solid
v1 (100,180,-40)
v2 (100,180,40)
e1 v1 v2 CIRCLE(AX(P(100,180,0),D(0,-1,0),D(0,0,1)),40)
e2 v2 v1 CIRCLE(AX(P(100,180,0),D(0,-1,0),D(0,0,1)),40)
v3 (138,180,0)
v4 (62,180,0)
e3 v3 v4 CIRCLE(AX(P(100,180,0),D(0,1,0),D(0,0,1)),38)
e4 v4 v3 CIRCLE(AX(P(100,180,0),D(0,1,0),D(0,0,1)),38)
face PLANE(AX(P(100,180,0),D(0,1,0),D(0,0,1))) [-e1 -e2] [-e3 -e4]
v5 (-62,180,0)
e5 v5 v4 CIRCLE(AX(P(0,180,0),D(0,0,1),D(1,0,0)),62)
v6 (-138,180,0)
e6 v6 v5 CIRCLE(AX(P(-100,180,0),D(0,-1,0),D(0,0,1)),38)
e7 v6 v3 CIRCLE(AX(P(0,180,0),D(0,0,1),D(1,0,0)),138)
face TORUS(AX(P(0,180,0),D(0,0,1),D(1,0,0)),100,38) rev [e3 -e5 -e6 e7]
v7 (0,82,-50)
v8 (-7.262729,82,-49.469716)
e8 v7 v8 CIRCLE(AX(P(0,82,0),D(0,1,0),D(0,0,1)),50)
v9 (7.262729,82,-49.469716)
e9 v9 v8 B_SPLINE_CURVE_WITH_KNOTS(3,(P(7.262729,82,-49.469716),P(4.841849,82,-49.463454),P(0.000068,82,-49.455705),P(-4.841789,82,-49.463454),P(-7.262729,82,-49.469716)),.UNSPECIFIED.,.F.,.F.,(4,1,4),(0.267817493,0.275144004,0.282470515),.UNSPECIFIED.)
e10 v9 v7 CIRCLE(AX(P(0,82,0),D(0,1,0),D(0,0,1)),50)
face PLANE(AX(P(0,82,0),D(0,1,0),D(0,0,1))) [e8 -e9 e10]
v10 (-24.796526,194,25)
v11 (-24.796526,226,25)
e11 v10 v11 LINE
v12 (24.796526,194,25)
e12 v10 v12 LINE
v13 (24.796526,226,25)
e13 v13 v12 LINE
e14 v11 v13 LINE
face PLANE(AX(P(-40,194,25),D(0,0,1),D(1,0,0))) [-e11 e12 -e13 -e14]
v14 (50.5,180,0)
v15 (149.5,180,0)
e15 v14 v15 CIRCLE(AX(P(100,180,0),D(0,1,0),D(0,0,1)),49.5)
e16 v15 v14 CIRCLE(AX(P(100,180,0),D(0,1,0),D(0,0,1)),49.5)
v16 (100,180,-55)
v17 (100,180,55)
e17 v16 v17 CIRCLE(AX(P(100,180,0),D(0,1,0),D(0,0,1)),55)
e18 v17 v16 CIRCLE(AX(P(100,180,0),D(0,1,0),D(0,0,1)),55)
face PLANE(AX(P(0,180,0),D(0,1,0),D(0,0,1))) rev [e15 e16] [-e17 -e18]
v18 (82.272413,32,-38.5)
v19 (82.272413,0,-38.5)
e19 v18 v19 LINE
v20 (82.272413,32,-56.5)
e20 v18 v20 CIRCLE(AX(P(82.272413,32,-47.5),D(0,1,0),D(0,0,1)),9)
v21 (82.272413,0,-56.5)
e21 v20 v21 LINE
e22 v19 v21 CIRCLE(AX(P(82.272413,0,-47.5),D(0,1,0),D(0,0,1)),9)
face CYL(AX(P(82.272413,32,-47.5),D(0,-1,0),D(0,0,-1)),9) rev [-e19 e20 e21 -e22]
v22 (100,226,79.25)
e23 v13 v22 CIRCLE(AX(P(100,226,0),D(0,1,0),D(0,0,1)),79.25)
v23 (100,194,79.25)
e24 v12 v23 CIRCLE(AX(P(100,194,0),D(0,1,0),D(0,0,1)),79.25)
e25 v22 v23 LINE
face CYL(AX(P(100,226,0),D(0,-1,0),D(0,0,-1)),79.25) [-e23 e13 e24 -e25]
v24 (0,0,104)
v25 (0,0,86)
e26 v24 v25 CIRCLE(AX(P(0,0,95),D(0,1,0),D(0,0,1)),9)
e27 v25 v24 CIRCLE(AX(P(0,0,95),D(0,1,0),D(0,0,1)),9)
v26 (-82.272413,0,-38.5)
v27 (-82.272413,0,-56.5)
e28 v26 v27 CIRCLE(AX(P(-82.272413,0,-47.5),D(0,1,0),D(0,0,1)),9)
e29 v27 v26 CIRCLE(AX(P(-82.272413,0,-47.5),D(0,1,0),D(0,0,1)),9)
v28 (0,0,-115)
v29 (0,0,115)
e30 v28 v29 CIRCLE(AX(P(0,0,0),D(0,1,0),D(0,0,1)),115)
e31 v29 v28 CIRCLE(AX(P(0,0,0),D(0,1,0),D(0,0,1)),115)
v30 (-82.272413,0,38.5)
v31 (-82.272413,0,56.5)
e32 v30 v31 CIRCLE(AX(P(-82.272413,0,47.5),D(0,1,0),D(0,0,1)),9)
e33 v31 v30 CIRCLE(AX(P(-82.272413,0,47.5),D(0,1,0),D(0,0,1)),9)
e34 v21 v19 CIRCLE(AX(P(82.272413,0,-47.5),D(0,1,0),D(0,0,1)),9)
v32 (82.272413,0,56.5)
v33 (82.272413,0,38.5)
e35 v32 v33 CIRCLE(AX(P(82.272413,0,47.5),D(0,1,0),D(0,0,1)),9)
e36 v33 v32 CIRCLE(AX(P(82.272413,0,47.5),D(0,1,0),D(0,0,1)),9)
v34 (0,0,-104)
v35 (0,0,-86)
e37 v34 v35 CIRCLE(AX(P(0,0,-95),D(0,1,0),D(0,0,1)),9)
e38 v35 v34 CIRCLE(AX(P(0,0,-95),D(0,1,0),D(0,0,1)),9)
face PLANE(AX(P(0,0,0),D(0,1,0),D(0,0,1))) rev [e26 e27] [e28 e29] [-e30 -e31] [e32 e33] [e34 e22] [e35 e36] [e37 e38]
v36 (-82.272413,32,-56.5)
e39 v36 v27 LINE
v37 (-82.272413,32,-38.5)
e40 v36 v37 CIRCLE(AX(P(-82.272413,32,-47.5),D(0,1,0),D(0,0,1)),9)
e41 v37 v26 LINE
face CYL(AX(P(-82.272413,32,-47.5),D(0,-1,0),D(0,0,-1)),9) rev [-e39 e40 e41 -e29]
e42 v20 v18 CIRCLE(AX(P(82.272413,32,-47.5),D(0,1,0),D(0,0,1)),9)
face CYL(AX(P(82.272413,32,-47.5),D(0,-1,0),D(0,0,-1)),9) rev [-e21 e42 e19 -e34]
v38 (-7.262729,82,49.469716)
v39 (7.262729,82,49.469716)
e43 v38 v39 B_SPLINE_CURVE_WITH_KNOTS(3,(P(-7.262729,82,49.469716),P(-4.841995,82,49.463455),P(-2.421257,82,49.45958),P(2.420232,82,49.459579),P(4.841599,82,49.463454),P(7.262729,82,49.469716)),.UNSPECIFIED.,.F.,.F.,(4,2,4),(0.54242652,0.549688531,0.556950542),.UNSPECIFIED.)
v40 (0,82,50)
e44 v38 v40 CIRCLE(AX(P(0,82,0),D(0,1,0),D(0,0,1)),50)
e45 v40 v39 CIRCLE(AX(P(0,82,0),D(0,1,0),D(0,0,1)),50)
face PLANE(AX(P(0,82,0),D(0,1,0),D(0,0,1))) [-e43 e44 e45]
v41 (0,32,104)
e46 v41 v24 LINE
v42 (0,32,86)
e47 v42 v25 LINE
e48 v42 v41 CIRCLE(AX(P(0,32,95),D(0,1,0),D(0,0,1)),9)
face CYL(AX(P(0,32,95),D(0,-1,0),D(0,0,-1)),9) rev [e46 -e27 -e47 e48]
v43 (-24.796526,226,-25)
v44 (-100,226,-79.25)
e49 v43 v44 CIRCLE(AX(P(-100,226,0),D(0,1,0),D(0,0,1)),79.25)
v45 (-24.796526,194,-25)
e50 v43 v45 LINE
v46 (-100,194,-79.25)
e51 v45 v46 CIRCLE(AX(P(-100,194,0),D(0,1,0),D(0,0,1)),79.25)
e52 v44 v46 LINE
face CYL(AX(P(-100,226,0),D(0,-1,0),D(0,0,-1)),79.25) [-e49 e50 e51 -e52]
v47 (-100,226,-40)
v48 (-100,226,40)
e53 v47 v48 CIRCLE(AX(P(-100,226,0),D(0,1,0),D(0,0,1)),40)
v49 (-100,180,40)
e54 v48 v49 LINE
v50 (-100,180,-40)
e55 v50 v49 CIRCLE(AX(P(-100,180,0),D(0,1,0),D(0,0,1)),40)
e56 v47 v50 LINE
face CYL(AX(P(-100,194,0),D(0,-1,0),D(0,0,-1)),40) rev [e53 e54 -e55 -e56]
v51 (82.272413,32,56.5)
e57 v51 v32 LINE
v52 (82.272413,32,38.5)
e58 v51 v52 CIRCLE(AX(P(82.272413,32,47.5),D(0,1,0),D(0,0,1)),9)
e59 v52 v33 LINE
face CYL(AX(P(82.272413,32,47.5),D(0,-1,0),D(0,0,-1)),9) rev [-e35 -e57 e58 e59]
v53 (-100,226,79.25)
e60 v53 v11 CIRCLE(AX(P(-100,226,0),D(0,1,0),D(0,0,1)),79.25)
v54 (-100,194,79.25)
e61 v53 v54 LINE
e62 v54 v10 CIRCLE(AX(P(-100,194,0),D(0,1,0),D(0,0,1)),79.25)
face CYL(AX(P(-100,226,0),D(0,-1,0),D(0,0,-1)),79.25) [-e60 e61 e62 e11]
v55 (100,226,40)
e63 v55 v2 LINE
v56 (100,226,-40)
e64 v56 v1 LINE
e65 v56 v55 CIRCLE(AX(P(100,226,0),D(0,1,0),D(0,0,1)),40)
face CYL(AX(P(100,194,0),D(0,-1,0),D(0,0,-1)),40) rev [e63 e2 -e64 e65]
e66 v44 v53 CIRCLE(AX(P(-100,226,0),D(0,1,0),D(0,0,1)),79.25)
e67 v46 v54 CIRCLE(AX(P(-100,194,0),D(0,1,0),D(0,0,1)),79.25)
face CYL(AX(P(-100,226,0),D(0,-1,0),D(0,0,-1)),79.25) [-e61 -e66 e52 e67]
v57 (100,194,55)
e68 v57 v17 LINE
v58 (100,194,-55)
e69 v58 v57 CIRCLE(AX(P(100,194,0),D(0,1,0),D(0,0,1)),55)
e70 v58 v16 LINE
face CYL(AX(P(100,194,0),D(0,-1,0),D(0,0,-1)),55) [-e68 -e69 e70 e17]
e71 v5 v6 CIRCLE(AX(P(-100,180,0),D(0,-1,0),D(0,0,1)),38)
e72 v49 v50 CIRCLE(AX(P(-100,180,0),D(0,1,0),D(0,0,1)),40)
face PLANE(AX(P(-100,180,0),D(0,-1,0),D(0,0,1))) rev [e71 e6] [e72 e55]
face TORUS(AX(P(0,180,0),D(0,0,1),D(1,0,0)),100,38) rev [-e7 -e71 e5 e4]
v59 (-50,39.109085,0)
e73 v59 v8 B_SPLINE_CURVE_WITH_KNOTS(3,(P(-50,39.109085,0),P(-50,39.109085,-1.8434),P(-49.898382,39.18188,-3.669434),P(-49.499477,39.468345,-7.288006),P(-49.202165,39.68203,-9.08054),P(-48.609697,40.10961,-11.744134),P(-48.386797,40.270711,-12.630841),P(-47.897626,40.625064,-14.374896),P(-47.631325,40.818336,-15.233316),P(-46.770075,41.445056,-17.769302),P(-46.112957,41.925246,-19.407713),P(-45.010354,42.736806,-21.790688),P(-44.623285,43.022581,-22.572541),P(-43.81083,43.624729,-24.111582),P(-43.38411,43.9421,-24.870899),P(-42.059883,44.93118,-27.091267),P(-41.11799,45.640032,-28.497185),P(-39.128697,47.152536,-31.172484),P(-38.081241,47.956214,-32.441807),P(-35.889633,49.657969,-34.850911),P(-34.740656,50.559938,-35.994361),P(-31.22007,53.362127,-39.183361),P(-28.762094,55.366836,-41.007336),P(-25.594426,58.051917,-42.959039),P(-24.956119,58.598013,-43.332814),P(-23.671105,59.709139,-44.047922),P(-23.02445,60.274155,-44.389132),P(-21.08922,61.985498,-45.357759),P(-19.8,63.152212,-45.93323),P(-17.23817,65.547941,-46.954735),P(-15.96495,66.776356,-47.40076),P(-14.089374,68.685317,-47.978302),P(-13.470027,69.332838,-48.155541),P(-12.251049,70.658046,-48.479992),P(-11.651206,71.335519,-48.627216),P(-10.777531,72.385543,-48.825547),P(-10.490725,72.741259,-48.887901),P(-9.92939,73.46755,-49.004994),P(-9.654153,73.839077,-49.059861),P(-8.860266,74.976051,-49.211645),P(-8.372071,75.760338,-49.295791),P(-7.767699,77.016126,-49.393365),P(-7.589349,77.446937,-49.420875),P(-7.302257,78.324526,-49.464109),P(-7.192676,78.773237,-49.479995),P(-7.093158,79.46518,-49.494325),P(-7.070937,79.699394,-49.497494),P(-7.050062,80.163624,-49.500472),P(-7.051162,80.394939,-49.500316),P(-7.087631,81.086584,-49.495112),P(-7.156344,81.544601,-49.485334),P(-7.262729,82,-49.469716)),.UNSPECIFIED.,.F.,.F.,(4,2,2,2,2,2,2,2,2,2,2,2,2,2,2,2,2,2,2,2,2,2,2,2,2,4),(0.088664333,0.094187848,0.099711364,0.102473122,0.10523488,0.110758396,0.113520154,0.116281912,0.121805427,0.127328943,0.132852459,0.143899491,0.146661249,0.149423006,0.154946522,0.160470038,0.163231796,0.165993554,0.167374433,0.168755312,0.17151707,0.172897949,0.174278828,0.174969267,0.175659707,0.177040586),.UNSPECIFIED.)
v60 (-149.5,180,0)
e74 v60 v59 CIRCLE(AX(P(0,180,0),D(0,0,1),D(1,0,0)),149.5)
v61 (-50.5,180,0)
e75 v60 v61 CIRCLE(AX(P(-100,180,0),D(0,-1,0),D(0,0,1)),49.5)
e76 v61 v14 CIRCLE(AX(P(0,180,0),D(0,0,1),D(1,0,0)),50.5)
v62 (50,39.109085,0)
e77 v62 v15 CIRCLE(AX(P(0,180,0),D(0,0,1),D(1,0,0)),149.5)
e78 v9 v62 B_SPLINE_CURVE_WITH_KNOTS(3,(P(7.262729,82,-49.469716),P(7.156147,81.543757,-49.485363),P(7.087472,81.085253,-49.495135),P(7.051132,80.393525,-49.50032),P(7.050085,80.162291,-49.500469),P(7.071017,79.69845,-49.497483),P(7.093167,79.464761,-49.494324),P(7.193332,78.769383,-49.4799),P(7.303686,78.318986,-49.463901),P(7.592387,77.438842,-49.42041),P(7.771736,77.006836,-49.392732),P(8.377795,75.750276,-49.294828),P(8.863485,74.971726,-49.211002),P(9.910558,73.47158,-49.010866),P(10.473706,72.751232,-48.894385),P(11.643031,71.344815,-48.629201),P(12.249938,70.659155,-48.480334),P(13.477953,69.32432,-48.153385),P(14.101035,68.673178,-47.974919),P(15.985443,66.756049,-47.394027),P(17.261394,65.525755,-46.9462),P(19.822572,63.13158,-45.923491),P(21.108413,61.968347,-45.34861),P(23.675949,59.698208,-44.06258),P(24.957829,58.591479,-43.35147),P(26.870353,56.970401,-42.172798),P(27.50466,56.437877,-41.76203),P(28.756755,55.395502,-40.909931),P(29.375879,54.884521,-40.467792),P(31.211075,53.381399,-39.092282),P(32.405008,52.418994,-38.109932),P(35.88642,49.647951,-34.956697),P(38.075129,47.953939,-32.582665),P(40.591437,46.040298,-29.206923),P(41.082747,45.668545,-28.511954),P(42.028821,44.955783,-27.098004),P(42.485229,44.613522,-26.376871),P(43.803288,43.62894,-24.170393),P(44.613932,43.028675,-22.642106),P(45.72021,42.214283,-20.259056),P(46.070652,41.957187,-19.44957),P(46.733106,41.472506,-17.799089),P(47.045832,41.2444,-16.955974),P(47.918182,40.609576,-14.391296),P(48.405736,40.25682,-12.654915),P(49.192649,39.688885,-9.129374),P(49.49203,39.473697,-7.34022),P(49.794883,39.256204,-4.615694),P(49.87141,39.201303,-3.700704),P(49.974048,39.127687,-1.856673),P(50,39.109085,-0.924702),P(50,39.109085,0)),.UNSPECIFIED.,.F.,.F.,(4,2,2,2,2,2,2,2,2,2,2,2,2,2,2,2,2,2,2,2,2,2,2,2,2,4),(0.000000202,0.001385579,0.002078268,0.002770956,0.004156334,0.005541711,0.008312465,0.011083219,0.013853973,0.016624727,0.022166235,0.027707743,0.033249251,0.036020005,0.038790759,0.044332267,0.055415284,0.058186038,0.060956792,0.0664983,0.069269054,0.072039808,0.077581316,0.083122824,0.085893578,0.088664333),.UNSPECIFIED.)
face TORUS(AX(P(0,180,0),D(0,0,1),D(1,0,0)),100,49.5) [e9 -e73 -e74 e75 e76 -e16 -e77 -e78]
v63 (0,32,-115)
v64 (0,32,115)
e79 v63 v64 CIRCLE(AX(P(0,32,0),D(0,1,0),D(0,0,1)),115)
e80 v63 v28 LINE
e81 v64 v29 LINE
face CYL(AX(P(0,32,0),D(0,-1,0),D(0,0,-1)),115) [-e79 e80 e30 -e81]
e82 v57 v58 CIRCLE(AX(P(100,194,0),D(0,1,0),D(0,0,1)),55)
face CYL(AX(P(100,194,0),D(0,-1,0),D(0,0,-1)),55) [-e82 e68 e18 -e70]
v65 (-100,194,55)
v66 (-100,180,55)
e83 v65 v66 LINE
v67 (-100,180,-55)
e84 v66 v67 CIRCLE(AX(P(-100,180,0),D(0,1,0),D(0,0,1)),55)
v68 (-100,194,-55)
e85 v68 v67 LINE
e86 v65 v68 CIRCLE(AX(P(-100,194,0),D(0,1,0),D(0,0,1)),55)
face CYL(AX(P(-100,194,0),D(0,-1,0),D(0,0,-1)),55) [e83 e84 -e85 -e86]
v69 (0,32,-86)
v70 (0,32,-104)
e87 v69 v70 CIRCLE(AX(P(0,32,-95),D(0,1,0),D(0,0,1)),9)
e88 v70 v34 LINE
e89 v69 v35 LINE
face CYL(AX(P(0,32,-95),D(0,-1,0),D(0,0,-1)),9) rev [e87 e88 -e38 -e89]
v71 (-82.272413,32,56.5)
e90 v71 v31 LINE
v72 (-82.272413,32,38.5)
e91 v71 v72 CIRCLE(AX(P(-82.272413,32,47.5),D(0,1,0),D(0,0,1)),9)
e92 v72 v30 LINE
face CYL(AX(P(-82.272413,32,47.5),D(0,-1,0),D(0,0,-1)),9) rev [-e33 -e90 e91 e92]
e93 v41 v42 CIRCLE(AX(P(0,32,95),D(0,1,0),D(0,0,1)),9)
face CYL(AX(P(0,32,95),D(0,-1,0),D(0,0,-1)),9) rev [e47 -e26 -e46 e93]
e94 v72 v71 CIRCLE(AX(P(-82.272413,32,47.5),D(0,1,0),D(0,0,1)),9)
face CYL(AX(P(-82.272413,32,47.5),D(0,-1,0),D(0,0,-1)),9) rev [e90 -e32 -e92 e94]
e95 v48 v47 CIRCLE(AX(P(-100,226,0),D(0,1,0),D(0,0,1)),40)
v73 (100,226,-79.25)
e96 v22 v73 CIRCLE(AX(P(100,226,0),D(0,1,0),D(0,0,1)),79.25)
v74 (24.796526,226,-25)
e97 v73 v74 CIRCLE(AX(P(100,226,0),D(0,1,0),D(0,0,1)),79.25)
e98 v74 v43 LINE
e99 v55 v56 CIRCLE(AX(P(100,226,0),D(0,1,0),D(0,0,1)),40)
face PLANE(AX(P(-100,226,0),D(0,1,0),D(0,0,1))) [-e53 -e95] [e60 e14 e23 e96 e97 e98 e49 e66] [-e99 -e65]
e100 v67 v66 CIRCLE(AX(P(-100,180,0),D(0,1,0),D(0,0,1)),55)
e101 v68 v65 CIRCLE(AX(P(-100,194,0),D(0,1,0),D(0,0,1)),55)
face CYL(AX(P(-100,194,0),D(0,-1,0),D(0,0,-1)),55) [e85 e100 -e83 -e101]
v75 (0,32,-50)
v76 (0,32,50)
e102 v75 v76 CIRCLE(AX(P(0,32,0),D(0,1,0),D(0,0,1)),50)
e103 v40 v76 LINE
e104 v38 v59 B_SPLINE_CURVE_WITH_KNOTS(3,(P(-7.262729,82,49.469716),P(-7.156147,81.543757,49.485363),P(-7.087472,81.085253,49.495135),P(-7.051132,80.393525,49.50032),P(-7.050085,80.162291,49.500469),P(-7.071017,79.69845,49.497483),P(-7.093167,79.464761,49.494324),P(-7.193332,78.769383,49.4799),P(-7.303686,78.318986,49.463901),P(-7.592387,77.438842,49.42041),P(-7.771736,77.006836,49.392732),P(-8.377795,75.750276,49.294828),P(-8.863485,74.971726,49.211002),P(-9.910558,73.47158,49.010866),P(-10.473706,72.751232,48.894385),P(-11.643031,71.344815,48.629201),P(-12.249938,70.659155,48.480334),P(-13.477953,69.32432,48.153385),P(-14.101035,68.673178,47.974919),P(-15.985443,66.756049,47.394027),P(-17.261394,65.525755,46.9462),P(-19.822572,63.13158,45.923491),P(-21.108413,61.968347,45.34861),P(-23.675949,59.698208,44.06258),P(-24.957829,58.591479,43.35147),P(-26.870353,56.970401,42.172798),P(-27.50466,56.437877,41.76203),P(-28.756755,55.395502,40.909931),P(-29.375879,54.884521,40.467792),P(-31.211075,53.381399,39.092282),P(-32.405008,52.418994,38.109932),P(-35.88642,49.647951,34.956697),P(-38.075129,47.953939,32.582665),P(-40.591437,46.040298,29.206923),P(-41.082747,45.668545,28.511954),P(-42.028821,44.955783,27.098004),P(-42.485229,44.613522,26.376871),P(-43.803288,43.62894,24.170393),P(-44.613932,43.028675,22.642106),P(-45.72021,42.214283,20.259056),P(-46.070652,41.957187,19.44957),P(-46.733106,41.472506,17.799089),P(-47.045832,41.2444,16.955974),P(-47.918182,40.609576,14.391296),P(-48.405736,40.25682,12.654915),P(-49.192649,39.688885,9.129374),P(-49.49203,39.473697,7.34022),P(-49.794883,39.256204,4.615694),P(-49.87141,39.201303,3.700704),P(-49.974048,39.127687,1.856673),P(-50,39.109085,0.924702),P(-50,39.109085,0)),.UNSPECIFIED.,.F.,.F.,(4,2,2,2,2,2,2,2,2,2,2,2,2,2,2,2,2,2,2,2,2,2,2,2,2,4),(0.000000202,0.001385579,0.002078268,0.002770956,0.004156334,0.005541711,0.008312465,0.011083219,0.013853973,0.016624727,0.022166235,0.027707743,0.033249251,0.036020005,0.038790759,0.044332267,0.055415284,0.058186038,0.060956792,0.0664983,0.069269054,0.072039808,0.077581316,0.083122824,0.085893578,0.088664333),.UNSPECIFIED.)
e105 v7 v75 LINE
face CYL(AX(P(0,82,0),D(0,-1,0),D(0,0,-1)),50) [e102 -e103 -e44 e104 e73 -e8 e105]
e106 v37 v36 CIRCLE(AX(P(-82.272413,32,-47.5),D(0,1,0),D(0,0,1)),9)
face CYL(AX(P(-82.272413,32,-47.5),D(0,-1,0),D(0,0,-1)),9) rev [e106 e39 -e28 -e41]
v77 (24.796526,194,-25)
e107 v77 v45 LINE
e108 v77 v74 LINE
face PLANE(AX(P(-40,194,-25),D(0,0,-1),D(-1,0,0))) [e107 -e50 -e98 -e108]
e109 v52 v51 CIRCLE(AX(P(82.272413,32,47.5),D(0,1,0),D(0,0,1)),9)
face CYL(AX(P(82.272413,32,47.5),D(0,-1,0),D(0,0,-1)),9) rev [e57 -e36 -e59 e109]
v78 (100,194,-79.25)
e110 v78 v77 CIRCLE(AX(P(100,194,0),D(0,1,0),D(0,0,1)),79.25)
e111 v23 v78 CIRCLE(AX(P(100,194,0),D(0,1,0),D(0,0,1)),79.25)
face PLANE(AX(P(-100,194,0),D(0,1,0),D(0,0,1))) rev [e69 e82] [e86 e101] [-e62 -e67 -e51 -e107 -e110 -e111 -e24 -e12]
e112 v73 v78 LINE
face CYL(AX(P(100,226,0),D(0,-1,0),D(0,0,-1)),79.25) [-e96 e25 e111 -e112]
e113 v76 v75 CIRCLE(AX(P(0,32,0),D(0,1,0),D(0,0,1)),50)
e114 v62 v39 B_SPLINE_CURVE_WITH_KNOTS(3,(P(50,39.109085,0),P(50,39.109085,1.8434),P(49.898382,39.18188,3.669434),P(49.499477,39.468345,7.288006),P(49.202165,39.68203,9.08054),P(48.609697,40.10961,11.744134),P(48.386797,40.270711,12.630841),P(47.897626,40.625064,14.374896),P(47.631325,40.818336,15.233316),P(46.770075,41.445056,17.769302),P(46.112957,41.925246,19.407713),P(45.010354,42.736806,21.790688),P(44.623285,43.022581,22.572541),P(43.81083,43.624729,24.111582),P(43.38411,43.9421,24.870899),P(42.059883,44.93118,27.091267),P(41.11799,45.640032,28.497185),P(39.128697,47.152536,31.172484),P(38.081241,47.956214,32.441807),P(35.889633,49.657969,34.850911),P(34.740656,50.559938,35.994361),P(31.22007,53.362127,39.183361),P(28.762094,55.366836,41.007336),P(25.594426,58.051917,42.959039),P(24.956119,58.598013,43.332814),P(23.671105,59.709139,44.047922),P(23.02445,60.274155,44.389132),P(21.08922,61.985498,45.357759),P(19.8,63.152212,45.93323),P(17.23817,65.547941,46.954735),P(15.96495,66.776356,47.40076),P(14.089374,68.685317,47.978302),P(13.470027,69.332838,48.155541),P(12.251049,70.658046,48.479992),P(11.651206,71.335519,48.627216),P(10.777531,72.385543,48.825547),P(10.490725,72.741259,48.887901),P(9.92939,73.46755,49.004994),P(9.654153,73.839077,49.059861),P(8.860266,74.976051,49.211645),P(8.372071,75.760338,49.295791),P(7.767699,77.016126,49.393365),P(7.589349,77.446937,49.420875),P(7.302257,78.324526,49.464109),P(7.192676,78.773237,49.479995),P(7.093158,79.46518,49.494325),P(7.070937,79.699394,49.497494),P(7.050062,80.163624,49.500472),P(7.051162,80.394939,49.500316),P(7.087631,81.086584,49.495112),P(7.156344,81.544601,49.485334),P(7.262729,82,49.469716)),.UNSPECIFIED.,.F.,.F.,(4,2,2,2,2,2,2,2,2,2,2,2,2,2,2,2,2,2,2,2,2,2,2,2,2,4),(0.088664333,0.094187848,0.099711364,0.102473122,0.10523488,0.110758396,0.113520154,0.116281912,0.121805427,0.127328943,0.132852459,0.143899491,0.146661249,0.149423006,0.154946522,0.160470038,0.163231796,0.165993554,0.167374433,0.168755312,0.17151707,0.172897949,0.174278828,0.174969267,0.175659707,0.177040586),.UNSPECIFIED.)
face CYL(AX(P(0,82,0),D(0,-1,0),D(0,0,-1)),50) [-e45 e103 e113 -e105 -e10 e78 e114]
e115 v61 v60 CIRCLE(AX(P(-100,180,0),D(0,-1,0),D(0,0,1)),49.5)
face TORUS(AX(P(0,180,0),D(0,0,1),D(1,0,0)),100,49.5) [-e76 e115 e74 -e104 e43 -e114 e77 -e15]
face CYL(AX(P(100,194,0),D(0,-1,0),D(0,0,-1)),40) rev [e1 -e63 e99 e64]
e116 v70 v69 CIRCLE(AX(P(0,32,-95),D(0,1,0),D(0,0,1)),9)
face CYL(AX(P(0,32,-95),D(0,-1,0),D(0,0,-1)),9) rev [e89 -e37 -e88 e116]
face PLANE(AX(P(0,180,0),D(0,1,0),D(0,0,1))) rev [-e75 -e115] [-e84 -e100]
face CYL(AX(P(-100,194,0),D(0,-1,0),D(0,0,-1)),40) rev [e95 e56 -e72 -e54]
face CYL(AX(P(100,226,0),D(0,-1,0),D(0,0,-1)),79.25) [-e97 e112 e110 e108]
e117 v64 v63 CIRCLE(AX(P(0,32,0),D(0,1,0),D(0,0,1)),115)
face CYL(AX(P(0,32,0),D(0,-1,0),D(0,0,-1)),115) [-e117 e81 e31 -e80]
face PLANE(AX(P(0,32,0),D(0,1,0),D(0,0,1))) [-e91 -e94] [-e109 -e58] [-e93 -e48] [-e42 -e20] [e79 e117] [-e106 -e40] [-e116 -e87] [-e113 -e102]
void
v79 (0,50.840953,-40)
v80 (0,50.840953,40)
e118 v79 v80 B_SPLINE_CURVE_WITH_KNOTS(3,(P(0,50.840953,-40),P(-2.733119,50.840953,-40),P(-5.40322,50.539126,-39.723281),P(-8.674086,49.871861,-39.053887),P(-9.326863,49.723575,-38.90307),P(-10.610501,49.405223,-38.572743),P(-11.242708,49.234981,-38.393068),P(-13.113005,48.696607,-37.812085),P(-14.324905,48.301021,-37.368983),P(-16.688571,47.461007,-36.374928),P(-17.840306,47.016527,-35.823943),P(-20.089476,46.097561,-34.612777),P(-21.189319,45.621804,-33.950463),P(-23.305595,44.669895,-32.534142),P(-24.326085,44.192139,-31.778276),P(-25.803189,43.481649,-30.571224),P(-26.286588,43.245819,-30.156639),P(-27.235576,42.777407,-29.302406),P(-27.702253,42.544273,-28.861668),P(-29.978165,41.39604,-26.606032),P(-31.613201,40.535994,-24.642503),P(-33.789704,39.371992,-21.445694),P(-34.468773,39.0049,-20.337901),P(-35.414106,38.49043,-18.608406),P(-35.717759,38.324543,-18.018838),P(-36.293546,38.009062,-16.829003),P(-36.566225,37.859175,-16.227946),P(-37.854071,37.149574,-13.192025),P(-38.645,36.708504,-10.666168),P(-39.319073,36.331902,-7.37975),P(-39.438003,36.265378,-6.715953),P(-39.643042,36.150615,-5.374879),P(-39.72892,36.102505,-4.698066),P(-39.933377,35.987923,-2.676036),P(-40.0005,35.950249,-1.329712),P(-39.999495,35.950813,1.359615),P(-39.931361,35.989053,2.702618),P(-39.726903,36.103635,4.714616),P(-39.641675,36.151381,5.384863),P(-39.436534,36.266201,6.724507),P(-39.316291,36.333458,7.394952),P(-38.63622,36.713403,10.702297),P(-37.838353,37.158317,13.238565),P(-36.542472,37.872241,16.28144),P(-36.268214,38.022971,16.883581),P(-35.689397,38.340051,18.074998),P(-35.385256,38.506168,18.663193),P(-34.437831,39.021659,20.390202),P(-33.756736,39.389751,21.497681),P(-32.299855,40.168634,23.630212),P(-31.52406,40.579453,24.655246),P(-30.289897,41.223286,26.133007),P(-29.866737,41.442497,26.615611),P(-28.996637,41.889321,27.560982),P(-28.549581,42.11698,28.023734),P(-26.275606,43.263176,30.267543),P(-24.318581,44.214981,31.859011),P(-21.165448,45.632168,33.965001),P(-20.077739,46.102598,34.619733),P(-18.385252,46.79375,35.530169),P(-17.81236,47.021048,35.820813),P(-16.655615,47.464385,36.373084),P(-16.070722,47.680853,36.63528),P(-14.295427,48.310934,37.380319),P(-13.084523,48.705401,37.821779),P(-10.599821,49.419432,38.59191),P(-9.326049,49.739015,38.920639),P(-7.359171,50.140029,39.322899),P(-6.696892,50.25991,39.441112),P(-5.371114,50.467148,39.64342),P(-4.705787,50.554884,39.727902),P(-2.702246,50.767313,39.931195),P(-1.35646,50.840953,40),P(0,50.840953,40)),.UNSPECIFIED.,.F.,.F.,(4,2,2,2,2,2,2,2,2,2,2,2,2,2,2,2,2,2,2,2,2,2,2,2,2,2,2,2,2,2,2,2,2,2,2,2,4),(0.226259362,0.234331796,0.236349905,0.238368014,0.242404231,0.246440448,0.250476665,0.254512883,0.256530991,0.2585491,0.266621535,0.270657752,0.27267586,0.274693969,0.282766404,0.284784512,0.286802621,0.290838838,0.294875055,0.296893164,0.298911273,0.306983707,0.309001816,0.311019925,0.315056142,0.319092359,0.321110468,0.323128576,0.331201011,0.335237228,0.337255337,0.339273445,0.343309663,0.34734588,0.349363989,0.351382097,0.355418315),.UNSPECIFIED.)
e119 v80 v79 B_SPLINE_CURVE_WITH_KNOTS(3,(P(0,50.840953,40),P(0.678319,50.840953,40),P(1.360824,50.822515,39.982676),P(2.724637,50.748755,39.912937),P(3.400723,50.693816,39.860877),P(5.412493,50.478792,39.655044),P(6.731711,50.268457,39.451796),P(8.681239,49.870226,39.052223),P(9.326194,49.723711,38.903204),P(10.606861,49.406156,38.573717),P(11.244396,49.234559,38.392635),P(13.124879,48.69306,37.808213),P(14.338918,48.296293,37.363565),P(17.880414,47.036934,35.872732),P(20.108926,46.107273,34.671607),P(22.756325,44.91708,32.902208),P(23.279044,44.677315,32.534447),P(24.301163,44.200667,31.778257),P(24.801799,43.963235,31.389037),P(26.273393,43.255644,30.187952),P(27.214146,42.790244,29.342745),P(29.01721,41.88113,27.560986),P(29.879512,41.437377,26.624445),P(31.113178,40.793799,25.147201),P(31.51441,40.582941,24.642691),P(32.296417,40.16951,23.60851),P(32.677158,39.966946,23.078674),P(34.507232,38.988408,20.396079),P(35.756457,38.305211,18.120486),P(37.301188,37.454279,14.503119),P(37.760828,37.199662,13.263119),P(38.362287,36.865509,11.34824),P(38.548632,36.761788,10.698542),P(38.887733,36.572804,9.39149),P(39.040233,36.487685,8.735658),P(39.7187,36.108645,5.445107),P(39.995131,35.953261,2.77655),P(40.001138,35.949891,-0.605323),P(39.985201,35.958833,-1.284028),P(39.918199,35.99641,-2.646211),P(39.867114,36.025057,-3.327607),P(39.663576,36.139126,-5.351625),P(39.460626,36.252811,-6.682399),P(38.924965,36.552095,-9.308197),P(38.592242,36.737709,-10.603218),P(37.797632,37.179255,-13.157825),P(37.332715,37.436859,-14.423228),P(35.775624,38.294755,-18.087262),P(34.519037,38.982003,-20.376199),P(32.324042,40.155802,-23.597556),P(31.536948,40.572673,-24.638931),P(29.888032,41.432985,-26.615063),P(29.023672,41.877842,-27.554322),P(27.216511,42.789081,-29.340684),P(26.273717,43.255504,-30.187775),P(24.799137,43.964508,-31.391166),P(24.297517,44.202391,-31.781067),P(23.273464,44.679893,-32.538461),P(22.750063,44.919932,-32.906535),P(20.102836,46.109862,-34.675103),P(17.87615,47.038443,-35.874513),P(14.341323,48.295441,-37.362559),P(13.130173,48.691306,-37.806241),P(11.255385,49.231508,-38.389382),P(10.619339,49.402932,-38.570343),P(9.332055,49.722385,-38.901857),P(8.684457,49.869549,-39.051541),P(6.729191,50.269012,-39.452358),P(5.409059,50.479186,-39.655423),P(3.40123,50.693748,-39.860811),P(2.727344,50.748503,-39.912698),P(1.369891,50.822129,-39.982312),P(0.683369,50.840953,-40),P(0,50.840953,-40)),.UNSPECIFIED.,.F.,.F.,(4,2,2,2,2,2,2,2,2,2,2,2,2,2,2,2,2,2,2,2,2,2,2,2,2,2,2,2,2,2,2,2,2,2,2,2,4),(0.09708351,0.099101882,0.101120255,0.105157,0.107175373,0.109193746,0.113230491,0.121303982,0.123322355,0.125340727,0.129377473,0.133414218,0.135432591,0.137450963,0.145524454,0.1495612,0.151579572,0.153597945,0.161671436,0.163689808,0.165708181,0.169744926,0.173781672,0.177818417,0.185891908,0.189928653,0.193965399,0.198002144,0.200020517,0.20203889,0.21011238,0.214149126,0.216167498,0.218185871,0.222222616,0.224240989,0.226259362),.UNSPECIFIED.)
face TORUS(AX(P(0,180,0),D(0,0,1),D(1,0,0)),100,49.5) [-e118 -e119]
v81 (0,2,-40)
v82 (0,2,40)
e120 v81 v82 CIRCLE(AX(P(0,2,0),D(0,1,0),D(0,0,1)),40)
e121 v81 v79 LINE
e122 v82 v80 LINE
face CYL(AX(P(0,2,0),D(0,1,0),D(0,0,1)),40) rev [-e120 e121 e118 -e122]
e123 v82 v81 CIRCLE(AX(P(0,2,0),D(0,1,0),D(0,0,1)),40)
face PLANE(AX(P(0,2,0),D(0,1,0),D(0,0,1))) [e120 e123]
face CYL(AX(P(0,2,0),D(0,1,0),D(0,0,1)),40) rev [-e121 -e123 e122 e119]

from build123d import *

# Parameters (mm, degrees)
BASE_FLANGE_SKETCH_R       = 115
BASE_FLANGE_SKETCH_R_2     = 9
BASE_FLANGE_6X_18_DEPTH    = 32
INLET_BORE_SKETCH_R        = 40
INLET_BORE_80_DEPTH        = 30
INLET_START                = 50
INLET_NECK_SKETCH_R        = 50
INLET_NECK_SKETCH_R_2      = 40
INLET_NECK_100_DEPTH       = 50
BRANCH_PROFILE_SKETCH_R    = 49.5
BRANCH_PROFILE_SKETCH_R_2  = 38
OUTLET_PAD_SKETCH_R        = 55
OUTLET_PAD_SKETCH_R_2      = 49.5
OUTLET_PAD_SKETCH_R_3      = 40
OUTLET_PADS_DEPTH          = 14
OUTLET_FLANGE_SKETCH_R     = 79.25
OUTLET_FLANGE_SKETCH_R_2   = 40
OUTLET_FLANGES_158_5_DEPTH = 32
FLANGE_BRIDGE_SKETCH_W     = 80
FLANGE_BRIDGE_SKETCH_H     = 50
FLANGE_BRIDGE_DEPTH        = 32
BRANCH_BORE_SKETCH_R       = 38


with BuildPart() as part:
    # Base Flange Sketch → Base Flange 6x_18 (new body)
    with BuildSketch(Plane(origin=(0, 0, 0), x_dir=(1, 0, 0), z_dir=(0, 1, 0))):
        with Locations(Location((0, 0, 0), (0, 0, 270))):
            Circle(BASE_FLANGE_SKETCH_R)
        with Locations(Location((0, 95, 0), (0, 0, 270))):
            Circle(BASE_FLANGE_SKETCH_R_2, mode=Mode.SUBTRACT)
        with Locations(Location((82.27241336, 47.5, 0), (0, 0, 270))):
            Circle(BASE_FLANGE_SKETCH_R_2, mode=Mode.SUBTRACT)
        with Locations(Location((82.27241336, -47.5, 0), (0, 0, 270))):
            Circle(BASE_FLANGE_SKETCH_R_2, mode=Mode.SUBTRACT)
        with Locations(Location((0, -95, 0), (0, 0, 270))):
            Circle(BASE_FLANGE_SKETCH_R_2, mode=Mode.SUBTRACT)
        with Locations(Location((-82.27241336, -47.5, 0), (0, 0, 270))):
            Circle(BASE_FLANGE_SKETCH_R_2, mode=Mode.SUBTRACT)
        with Locations(Location((-82.27241336, 47.5, 0), (0, 0, 270))):
            Circle(BASE_FLANGE_SKETCH_R_2, mode=Mode.SUBTRACT)
    extrude(amount=BASE_FLANGE_6X_18_DEPTH)

    # Inlet Bore Sketch → Inlet Bore _80 (cut)
    with BuildSketch(Plane(origin=(0, 32, 0), x_dir=(1, 0, 0), z_dir=(0, 1, 0))):
        with Locations(Location((0, 0, 0), (0, 0, 270))):
            Circle(INLET_BORE_SKETCH_R)
    extrude(amount=-INLET_BORE_80_DEPTH, mode=Mode.SUBTRACT)

    # Inlet Neck Sketch → Inlet Neck _100 (add)
    with BuildSketch(Plane(origin=(0, 32, 0), x_dir=(1, 0, 0), z_dir=(0, 1, 0)).offset(INLET_START)):
        with Locations(Location((0, 0, 0), (0, 0, 270))):
            Circle(INLET_NECK_SKETCH_R)
        with Locations(Location((0, 0, 0), (0, 0, 270))):
            Circle(INLET_NECK_SKETCH_R_2, mode=Mode.SUBTRACT)
    extrude(amount=-INLET_NECK_100_DEPTH)

    # Branch Pipe Sweep: sweep along a path in Branch Path Sketch
    with BuildLine(Plane.XY) as branch_pipe_sweep_path:
        ThreePointArc((-100, 180), (0, 80), (100, 180))
    # Branch Profile Sketch → Branch Pipe Sweep (sweep)
    with BuildSketch(Plane(origin=(0, 180, 0), x_dir=(1, 0, 0), z_dir=(0, 1, 0))):
        with Locations((100, 0)):
            Circle(BRANCH_PROFILE_SKETCH_R)
        with Locations((100, 0)):
            Circle(BRANCH_PROFILE_SKETCH_R_2, mode=Mode.SUBTRACT)
    sweep(path=branch_pipe_sweep_path.line)

    # Outlet Pad Sketch → Outlet Pads (add)
    # profile 1 of 3: a face of its own
    with BuildSketch(Plane(origin=(0, 180, 0), x_dir=(1, 0, 0), z_dir=(0, 1, 0))):
        with Locations(Location((-100, 0, 0), (0, 0, 270))):
            Circle(OUTLET_PAD_SKETCH_R)
        with Locations((-100, 0)):
            Circle(OUTLET_PAD_SKETCH_R_2, mode=Mode.SUBTRACT)
    # profile 2 of 3: a face of its own
    with BuildSketch(Plane(origin=(0, 180, 0), x_dir=(1, 0, 0), z_dir=(0, 1, 0))):
        with Locations((-100, 0)):
            Circle(OUTLET_PAD_SKETCH_R_2)
        with Locations(Location((-100, 0, 0), (0, 0, 270))):
            Circle(OUTLET_PAD_SKETCH_R_3, mode=Mode.SUBTRACT)
    # profile 3 of 3: a face of its own
    with BuildSketch(Plane(origin=(0, 180, 0), x_dir=(1, 0, 0), z_dir=(0, 1, 0))):
        with Locations(Location((100, 0, 0), (0, 0, 270))):
            Circle(OUTLET_PAD_SKETCH_R)
        with Locations(Location((100, 0, 0), (0, 0, 270))):
            Circle(OUTLET_PAD_SKETCH_R_3, mode=Mode.SUBTRACT)
    extrude(amount=OUTLET_PADS_DEPTH)

    # Outlet Flange Sketch → Outlet Flanges _158.5 (add)
    # profile 1 of 2: a face of its own
    with BuildSketch(Plane(origin=(0, 194, 0), x_dir=(1, 0, 0), z_dir=(0, 1, 0))):
        with Locations(Location((-100, 0, 0), (0, 0, 270))):
            Circle(OUTLET_FLANGE_SKETCH_R)
        with Locations(Location((-100, 0, 0), (0, 0, 270))):
            Circle(OUTLET_FLANGE_SKETCH_R_2, mode=Mode.SUBTRACT)
    # profile 2 of 2: a face of its own
    with BuildSketch(Plane(origin=(0, 194, 0), x_dir=(1, 0, 0), z_dir=(0, 1, 0))):
        with Locations(Location((100, 0, 0), (0, 0, 270))):
            Circle(OUTLET_FLANGE_SKETCH_R)
        with Locations(Location((100, 0, 0), (0, 0, 270))):
            Circle(OUTLET_FLANGE_SKETCH_R_2, mode=Mode.SUBTRACT)
    extrude(amount=OUTLET_FLANGES_158_5_DEPTH)

    # Flange Bridge Sketch → Flange Bridge (add)
    with BuildSketch(Plane(origin=(0, 226, 0), x_dir=(1, 0, 0), z_dir=(0, 1, 0))):
        Rectangle(FLANGE_BRIDGE_SKETCH_W, FLANGE_BRIDGE_SKETCH_H)
    extrude(amount=-FLANGE_BRIDGE_DEPTH)

    # Branch Bore Sweep _76: sweep along a path in Sketch7_2
    with BuildLine(Plane.XY) as branch_bore_sweep_76_path:
        ThreePointArc((-100, 180), (0, 80), (100, 180))
    # Branch Bore Sketch → Branch Bore Sweep _76 (sweep, cut)
    with BuildSketch(Plane(origin=(0, 180, 0), x_dir=(1, 0, 0), z_dir=(0, 1, 0))):
        with Locations((-100, 0)):
            Circle(BRANCH_BORE_SKETCH_R)
    sweep(path=branch_bore_sweep_76_path.line, mode=Mode.SUBTRACT)


solid = part.part
